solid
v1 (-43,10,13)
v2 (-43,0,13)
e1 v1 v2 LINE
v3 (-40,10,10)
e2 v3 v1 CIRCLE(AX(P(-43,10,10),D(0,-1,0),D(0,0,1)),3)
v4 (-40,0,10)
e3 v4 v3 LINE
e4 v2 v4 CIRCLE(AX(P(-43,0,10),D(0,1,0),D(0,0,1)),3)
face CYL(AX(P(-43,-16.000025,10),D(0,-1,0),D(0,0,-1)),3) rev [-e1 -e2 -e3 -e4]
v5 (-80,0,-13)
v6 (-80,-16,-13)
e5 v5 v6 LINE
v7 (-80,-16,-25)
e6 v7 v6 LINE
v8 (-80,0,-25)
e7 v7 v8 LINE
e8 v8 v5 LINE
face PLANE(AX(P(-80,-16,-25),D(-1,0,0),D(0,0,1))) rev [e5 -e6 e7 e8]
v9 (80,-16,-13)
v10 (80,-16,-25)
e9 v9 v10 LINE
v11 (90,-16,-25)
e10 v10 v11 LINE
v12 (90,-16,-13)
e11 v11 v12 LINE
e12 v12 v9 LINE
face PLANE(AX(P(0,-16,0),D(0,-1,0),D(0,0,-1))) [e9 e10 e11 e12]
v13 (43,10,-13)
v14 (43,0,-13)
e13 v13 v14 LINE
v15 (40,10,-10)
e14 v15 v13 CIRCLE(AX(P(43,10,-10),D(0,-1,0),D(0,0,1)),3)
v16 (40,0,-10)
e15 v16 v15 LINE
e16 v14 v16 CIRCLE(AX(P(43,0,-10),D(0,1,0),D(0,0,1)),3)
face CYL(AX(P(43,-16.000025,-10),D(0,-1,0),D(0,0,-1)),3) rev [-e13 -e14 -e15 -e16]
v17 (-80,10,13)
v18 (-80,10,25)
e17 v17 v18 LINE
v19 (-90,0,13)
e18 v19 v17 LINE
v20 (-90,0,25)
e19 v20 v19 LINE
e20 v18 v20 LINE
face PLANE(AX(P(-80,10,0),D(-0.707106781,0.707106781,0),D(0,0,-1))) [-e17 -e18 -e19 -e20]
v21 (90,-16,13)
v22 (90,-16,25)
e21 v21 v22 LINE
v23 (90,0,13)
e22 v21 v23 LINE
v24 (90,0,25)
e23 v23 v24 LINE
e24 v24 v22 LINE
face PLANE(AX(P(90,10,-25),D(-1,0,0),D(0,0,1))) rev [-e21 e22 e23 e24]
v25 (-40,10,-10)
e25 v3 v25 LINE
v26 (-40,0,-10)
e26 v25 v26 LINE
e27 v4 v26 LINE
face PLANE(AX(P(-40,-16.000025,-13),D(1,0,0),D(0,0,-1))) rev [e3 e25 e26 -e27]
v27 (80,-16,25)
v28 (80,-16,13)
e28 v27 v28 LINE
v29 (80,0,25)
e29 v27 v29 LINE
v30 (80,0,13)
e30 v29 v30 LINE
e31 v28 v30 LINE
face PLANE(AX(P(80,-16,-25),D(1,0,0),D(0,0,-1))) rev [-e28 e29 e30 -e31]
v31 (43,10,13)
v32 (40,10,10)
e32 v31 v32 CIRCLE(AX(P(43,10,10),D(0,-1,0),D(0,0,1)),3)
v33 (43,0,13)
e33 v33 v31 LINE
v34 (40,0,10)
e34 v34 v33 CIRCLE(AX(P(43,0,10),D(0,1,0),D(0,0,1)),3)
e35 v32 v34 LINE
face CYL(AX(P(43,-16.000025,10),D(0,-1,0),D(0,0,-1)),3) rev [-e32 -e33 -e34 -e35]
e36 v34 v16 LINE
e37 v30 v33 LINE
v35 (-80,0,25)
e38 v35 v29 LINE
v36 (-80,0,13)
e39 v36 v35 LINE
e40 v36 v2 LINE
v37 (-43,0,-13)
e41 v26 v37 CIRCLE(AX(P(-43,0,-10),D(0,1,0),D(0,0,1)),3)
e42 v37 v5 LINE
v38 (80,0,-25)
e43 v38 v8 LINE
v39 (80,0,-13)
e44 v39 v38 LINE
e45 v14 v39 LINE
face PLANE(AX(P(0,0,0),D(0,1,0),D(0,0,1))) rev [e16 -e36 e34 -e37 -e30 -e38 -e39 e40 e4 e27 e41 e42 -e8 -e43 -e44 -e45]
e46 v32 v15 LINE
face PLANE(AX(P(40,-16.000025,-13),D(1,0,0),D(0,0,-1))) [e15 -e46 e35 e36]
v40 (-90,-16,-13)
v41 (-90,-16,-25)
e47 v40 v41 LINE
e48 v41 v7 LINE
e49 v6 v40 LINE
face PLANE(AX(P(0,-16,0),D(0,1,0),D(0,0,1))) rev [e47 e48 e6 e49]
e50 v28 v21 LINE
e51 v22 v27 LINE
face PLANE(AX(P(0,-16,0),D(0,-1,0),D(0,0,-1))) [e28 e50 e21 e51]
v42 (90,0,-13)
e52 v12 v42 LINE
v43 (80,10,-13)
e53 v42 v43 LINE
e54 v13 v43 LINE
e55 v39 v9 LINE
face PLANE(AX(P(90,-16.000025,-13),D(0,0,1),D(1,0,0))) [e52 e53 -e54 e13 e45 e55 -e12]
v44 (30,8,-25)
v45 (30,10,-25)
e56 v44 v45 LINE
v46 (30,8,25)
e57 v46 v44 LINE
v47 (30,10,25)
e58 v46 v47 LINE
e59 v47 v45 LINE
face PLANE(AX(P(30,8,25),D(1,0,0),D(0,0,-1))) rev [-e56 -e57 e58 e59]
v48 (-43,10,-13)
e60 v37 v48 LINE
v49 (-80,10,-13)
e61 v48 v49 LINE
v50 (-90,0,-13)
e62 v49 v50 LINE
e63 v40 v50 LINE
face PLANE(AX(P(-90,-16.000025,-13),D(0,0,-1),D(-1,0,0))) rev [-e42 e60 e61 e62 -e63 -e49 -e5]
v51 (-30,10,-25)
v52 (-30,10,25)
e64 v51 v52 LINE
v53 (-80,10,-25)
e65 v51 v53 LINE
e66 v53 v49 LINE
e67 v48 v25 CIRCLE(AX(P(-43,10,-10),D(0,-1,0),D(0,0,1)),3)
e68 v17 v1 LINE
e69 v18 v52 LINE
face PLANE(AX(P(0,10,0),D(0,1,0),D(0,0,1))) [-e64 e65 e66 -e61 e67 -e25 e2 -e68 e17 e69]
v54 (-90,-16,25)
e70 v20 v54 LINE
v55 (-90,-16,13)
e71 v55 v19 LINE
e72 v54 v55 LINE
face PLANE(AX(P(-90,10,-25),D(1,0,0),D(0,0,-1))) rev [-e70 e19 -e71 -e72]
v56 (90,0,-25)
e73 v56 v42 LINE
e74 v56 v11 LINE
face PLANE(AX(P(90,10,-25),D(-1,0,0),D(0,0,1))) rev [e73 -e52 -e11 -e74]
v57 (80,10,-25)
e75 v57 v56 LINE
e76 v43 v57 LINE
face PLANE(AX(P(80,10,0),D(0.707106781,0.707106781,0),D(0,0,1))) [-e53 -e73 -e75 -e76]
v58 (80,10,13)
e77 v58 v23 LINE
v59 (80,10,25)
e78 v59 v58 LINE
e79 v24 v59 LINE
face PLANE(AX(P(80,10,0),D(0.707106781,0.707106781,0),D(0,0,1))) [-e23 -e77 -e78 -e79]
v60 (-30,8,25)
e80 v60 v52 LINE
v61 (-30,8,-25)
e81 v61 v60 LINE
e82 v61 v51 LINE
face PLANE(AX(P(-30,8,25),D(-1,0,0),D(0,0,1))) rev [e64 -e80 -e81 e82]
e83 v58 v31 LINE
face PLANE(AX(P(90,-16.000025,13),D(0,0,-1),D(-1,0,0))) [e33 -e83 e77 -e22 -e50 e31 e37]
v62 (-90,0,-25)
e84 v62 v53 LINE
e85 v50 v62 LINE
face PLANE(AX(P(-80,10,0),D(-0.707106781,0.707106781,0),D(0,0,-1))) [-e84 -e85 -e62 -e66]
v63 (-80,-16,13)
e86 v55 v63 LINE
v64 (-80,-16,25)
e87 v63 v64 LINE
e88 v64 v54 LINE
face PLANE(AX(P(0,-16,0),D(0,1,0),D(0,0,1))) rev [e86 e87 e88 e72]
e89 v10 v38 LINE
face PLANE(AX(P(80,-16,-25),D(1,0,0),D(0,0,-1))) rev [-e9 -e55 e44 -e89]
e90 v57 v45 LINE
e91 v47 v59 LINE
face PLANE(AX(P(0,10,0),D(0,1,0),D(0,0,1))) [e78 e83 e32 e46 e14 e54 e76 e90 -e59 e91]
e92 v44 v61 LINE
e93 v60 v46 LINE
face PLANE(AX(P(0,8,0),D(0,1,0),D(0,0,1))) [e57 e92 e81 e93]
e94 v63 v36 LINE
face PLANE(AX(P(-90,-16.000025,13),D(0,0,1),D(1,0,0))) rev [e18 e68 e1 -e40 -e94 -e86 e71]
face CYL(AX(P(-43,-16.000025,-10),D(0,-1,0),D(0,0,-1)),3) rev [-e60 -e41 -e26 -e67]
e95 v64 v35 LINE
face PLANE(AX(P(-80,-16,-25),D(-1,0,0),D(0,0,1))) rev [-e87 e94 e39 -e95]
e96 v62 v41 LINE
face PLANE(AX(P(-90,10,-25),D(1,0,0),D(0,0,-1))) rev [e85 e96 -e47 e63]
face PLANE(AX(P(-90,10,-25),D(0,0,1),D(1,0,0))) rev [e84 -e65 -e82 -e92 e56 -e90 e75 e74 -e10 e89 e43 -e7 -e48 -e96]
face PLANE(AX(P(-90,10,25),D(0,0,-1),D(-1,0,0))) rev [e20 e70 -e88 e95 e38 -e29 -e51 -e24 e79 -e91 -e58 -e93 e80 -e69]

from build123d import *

# Parameters (mm, degrees)
SKETCH1_W           = 180
SKETCH1_H           = 50
BOSS_EXTRUDE1_DEPTH = 10
SKETCH2_W           = 10
SKETCH2_H           = 50
BOSS_EXTRUDE2_DEPTH = 16
SKETCH3_W           = 50
SKETCH3_H           = 26
CUT_EXTRUDE1_DEPTH  = 97.958754117
FILLET1_R           = 3
CHAMFER1_SIZE       = 10
SKETCH4_W           = 60
SKETCH4_H           = 50
CUT_EXTRUDE2_DEPTH  = 2


with BuildPart() as part:
    # Sketch1 → Boss-Extrude1 (new body)
    with BuildSketch(Plane(origin=(0, 0, 0), x_dir=(1, 0, 0), z_dir=(0, 1, 0))):
        Rectangle(SKETCH1_W, SKETCH1_H)
    extrude(amount=BOSS_EXTRUDE1_DEPTH)

    # Sketch2 → Boss-Extrude2 (add)
    with BuildSketch(Plane.XZ):
        with Locations((-85, 0)):
            Rectangle(SKETCH2_W, SKETCH2_H)
        with Locations((85, 0)):
            Rectangle(SKETCH2_W, SKETCH2_H)
    extrude(amount=BOSS_EXTRUDE2_DEPTH)

    # Sketch3 → Cut-Extrude1 (cut, through all)
    with BuildSketch(Plane(origin=(0, 10, 0), x_dir=(1, 0, 0), z_dir=(0, 1, 0))):
        with Locations((-65, 0)):
            Rectangle(SKETCH3_W, SKETCH3_H)
    cut_extrude1 = extrude(amount=-CUT_EXTRUDE1_DEPTH, mode=Mode.SUBTRACT)

    # Mirror1: Cut-Extrude1 across plane
    add(cut_extrude1.mirror(Plane(origin=(0, 0, 0), x_dir=(0, 0, 1), z_dir=(1, 0, 0))), mode=Mode.SUBTRACT)

    # Fillet1
    fillet1_edges = [part.edges().sort_by_distance(p)[0] for p in [
        (-40, 5, -13),
        (-40, 5, 13),
        (40, 5, 13),
        (40, 5, -13),
    ]]
    fillet(fillet1_edges, radius=FILLET1_R)

    # Chamfer1
    chamfer1_edges = [part.edges().sort_by_distance(p)[0] for p in [
        (-90, 10, -19),
        (90, 10, 19),
        (-90, 10, 19),
        (90, 10, -19),
    ]]
    chamfer(chamfer1_edges, length=CHAMFER1_SIZE)

    # Sketch4 → Cut-Extrude2 (cut)
    with BuildSketch(Plane(origin=(0, 10, 0), x_dir=(1, 0, 0), z_dir=(0, 1, 0))):
        Rectangle(SKETCH4_W, SKETCH4_H)
    extrude(amount=-CUT_EXTRUDE2_DEPTH, mode=Mode.SUBTRACT)


solid = part.part
